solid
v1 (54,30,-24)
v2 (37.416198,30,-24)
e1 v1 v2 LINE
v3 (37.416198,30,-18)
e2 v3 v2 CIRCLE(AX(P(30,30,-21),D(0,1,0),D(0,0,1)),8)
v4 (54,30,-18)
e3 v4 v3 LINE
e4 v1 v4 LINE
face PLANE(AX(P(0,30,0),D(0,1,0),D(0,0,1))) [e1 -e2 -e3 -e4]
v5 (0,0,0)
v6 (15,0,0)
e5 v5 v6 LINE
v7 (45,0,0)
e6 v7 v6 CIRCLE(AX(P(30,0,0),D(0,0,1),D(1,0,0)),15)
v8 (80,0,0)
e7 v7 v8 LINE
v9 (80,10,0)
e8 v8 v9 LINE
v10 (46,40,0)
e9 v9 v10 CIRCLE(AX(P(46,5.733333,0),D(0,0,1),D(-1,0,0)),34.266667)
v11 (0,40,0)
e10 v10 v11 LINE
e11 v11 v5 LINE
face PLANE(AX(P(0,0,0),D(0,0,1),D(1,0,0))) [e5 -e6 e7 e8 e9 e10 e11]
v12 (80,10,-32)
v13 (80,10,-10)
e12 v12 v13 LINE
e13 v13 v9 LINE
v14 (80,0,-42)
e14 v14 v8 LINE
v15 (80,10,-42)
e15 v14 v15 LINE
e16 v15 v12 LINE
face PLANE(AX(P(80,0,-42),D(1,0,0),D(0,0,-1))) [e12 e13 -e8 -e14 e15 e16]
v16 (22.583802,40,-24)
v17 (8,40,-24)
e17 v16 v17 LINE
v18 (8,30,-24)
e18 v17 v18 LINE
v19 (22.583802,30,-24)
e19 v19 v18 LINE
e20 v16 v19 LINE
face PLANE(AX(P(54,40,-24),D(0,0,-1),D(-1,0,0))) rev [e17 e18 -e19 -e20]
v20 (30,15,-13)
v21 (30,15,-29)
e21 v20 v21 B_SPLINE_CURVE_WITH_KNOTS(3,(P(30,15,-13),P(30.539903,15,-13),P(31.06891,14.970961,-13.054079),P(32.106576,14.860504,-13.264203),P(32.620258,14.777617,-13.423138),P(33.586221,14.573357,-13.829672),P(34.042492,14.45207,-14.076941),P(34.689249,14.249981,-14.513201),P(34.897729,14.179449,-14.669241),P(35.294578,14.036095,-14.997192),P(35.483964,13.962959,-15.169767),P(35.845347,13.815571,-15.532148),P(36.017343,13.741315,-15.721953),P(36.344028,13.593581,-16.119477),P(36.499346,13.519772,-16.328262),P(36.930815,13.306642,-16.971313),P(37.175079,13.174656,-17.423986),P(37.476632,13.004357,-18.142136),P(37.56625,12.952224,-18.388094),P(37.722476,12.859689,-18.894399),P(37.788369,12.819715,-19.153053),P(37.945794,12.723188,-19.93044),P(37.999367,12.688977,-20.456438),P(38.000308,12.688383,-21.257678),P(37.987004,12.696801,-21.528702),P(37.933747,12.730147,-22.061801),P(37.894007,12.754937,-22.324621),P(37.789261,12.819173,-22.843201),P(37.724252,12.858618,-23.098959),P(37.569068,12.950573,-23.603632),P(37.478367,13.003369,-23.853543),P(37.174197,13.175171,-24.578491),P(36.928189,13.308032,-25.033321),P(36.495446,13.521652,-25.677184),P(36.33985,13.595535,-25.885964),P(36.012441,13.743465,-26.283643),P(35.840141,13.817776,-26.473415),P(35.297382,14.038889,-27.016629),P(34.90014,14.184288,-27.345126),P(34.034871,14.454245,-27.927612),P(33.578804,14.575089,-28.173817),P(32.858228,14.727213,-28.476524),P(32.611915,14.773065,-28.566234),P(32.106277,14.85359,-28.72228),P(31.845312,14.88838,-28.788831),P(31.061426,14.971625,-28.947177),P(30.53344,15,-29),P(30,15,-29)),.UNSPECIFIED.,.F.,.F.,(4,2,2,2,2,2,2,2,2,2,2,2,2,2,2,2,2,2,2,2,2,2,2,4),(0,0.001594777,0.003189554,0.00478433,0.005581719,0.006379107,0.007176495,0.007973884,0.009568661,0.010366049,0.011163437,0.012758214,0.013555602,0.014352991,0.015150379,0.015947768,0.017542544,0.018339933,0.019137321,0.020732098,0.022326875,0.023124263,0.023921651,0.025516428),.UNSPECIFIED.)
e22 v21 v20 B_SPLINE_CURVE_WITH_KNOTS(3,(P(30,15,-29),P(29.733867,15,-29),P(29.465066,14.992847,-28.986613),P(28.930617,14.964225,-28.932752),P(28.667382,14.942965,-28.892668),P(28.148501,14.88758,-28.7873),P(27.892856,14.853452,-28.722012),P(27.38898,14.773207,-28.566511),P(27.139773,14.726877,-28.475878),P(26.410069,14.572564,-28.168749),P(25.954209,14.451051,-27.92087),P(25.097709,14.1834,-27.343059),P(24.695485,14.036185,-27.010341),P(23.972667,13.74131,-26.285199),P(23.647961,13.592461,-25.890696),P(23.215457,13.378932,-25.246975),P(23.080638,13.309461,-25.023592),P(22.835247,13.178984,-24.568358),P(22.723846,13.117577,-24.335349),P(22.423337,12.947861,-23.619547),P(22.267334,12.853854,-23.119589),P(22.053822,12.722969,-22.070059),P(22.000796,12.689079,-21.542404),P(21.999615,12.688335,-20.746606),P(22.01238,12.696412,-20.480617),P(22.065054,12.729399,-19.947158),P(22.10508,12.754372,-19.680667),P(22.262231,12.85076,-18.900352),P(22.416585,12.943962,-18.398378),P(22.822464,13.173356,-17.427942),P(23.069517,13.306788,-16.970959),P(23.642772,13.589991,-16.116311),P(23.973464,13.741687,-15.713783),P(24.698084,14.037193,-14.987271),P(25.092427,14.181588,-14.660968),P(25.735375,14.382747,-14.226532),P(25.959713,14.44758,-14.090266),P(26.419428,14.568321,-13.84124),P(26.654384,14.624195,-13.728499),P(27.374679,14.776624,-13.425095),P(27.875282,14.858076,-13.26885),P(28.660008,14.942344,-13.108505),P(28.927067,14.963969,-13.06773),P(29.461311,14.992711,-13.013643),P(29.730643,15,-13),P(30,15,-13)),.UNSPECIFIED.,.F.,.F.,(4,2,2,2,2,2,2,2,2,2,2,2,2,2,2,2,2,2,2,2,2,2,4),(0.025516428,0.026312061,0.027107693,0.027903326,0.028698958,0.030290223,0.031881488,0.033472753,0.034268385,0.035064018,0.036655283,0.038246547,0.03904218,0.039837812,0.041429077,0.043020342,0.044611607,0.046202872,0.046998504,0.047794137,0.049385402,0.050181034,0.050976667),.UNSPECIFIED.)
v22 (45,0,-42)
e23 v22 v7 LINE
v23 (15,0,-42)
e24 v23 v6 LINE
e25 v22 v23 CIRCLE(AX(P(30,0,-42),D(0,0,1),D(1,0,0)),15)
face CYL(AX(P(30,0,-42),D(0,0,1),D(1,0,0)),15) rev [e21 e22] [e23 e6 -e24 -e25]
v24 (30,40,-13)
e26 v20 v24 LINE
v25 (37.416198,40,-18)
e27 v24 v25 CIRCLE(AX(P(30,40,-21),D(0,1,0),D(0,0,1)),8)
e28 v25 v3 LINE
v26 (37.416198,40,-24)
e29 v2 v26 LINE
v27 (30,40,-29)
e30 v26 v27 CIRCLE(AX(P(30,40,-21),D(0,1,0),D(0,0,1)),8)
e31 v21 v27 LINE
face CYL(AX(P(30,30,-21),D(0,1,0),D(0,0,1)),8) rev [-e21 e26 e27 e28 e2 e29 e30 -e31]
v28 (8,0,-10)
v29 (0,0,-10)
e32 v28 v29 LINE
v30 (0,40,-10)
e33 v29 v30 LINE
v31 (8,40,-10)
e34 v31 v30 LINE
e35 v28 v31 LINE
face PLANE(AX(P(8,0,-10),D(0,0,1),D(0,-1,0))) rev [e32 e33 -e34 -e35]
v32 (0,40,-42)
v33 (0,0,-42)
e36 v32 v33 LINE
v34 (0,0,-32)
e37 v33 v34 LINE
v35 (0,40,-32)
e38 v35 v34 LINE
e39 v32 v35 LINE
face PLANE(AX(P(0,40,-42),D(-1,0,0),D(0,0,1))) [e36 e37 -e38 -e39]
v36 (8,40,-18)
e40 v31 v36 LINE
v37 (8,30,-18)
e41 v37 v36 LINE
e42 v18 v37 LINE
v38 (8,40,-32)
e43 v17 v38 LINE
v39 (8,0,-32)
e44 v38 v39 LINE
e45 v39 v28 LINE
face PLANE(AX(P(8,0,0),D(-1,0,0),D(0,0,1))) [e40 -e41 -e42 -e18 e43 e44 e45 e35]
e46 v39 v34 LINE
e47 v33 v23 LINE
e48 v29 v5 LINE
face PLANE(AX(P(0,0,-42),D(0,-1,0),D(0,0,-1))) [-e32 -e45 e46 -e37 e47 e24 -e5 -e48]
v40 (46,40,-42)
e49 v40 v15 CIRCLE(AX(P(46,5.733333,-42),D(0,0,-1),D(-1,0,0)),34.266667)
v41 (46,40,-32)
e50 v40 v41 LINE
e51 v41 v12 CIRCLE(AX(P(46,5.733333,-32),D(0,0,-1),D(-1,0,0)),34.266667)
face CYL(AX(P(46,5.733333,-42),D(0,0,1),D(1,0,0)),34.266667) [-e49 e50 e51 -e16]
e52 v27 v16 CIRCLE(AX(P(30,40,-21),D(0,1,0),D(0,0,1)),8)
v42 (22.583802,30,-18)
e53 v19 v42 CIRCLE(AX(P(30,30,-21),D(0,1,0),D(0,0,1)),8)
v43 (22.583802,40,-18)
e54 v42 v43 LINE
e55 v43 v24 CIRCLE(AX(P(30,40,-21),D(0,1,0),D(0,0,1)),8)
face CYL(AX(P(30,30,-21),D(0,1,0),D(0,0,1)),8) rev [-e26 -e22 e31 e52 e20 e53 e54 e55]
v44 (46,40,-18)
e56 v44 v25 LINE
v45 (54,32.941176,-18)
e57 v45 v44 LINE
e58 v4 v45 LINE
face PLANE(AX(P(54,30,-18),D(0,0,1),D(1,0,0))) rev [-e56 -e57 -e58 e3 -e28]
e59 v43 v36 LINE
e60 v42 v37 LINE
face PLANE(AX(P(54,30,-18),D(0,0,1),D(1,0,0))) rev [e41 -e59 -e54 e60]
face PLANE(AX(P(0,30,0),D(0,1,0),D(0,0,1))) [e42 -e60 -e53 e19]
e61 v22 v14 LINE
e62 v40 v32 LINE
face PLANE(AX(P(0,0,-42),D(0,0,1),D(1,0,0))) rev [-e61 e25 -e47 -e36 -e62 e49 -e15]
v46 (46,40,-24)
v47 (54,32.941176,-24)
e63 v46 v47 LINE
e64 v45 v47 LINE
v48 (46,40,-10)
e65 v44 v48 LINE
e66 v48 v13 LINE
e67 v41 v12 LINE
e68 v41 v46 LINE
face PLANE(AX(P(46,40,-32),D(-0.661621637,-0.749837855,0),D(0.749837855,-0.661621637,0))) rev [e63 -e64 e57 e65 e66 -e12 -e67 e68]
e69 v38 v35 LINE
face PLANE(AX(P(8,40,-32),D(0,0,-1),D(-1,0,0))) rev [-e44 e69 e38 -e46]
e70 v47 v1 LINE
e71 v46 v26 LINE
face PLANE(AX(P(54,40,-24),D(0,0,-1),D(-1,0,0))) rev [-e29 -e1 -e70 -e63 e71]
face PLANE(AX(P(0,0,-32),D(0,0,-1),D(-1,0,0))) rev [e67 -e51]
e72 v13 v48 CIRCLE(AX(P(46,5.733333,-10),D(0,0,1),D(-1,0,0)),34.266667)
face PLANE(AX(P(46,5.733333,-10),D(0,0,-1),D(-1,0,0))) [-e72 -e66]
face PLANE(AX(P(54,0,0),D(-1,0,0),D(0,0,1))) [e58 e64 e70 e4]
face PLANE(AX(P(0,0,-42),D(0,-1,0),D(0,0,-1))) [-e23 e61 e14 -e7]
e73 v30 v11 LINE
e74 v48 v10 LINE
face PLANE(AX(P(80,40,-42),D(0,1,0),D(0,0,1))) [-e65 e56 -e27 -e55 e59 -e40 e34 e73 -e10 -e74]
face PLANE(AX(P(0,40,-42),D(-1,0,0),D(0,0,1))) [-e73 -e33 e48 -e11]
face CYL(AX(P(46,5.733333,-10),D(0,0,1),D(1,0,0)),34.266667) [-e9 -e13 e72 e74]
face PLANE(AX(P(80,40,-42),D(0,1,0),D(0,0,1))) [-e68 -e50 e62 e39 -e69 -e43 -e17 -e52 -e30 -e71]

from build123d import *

# Parameters (mm, degrees)
BASE_BLOCK_PROFILE_W        = 80
BASE_BLOCK_PROFILE_H        = 40
BASE_BLOCK_80X40X42_DEPTH   = 42
TOP_SLOT_PROFILE_W          = 34
TOP_SLOT_PROFILE_H          = 30
TOP_SLOT_CUT_10_DEPTH       = 10
GROOVE_CUT_22_DEPTH         = 22
GROOVE_INFILL_BOSS_10_DEPTH = 10
GROOVE_UNDERCUT_10_DEPTH    = 10
ROUNDED_END_CUT_DEPTH       = 42
ARCH_PROFILE_R              = 8
ARCH_CUT_10_DEPTH           = 10
SIDE_SLOT_PROFILE_W         = 22
SIDE_SLOT_PROFILE_H         = 40
SIDE_SLOT_CUT_8_DEPTH       = 8
INCLINED_SLOT_PROFILE_W     = 6
INCLINED_SLOT_PROFILE_H     = 10
INCLINED_SLOT_CUT_46_DEPTH  = 46
BORE_16_PROFILE_R           = 8
BORE_16_CUT_46_DEPTH        = 46


with BuildPart() as part:
    # Base Block Profile → Base Block 80x40x42 (new body)
    with BuildSketch(Plane.XY):
        with Locations((40, 20)):
            Rectangle(BASE_BLOCK_PROFILE_W, BASE_BLOCK_PROFILE_H)
    extrude(amount=-BASE_BLOCK_80X40X42_DEPTH)

    # Top Slot Profile → Top Slot Cut 10 (cut)
    with BuildSketch(Plane.XY):
        with Locations((63, 25)):
            Rectangle(TOP_SLOT_PROFILE_W, TOP_SLOT_PROFILE_H)
    extrude(amount=-TOP_SLOT_CUT_10_DEPTH, mode=Mode.SUBTRACT)

    # Groove Profile → Groove Cut 22 (cut)
    with BuildSketch(Plane.XY.offset(-10)):
        Polygon((46, 40), (80, 10), (80, 40), align=None)
    extrude(amount=-GROOVE_CUT_22_DEPTH, mode=Mode.SUBTRACT)

    # Groove Infill Profile → Groove Infill Boss 10 (add)
    with BuildSketch(Plane.XY):
        with BuildLine():
            Line((46, 40), (46, 10))
            Line((46, 10), (80, 10))
            ThreePointArc((80, 10), (68.671568098, 31.427777177), (46, 40))
        make_face()
    extrude(amount=-GROOVE_INFILL_BOSS_10_DEPTH)

    # Groove Undercut Profile → Groove Undercut 10 (cut)
    with BuildSketch(Plane.XY.offset(-32)):
        with BuildLine():
            Line((46, 40), (80, 40))
            Line((80, 40), (80, 10))
            ThreePointArc((80, 10), (68.671568098, 31.427777177), (46, 40))
        make_face()
    extrude(amount=-GROOVE_UNDERCUT_10_DEPTH, mode=Mode.SUBTRACT)

    # Rounded End Profile → Rounded End Cut (cut)
    with BuildSketch(Plane.XY):
        with BuildLine():
            ThreePointArc((45, 0), (30, 15), (15, 0))
            Line((15, 0), (30, 0))
            Line((30, 0), (45, 0))
        make_face()
    extrude(amount=-ROUNDED_END_CUT_DEPTH, mode=Mode.SUBTRACT)

    # Arch Profile → Arch Cut 10 (cut)
    with BuildSketch(Plane(origin=(0, 40, 0), x_dir=(1, 0, 0), z_dir=(0, 1, 0))):
        with Locations(Location((30, 21, 0), (0, 0, 270))):
            Circle(ARCH_PROFILE_R)
    extrude(amount=-ARCH_CUT_10_DEPTH, mode=Mode.SUBTRACT)

    # Side Slot Profile → Side Slot Cut 8 (cut)
    with BuildSketch(Plane.ZY):
        with Locations((-21, 20)):
            Rectangle(SIDE_SLOT_PROFILE_W, SIDE_SLOT_PROFILE_H)
    extrude(amount=-SIDE_SLOT_CUT_8_DEPTH, mode=Mode.SUBTRACT)

    # Inclined Slot Profile → Inclined Slot Cut 46 (cut)
    with BuildSketch(Plane.ZY.offset(-8)):
        with Locations((-21, 35)):
            Rectangle(INCLINED_SLOT_PROFILE_W, INCLINED_SLOT_PROFILE_H)
    extrude(amount=-INCLINED_SLOT_CUT_46_DEPTH, mode=Mode.SUBTRACT)

    # Bore Ø16 Profile → Bore Ø16 Cut 46 (cut)
    with BuildSketch(Plane(origin=(0, 30, 0), x_dir=(1, 0, 0), z_dir=(0, 1, 0))):
        with Locations(Location((30, 21, 0), (0, 0, 270))):
            Circle(BORE_16_PROFILE_R)
    extrude(amount=-BORE_16_CUT_46_DEPTH, mode=Mode.SUBTRACT)


solid = part.part
